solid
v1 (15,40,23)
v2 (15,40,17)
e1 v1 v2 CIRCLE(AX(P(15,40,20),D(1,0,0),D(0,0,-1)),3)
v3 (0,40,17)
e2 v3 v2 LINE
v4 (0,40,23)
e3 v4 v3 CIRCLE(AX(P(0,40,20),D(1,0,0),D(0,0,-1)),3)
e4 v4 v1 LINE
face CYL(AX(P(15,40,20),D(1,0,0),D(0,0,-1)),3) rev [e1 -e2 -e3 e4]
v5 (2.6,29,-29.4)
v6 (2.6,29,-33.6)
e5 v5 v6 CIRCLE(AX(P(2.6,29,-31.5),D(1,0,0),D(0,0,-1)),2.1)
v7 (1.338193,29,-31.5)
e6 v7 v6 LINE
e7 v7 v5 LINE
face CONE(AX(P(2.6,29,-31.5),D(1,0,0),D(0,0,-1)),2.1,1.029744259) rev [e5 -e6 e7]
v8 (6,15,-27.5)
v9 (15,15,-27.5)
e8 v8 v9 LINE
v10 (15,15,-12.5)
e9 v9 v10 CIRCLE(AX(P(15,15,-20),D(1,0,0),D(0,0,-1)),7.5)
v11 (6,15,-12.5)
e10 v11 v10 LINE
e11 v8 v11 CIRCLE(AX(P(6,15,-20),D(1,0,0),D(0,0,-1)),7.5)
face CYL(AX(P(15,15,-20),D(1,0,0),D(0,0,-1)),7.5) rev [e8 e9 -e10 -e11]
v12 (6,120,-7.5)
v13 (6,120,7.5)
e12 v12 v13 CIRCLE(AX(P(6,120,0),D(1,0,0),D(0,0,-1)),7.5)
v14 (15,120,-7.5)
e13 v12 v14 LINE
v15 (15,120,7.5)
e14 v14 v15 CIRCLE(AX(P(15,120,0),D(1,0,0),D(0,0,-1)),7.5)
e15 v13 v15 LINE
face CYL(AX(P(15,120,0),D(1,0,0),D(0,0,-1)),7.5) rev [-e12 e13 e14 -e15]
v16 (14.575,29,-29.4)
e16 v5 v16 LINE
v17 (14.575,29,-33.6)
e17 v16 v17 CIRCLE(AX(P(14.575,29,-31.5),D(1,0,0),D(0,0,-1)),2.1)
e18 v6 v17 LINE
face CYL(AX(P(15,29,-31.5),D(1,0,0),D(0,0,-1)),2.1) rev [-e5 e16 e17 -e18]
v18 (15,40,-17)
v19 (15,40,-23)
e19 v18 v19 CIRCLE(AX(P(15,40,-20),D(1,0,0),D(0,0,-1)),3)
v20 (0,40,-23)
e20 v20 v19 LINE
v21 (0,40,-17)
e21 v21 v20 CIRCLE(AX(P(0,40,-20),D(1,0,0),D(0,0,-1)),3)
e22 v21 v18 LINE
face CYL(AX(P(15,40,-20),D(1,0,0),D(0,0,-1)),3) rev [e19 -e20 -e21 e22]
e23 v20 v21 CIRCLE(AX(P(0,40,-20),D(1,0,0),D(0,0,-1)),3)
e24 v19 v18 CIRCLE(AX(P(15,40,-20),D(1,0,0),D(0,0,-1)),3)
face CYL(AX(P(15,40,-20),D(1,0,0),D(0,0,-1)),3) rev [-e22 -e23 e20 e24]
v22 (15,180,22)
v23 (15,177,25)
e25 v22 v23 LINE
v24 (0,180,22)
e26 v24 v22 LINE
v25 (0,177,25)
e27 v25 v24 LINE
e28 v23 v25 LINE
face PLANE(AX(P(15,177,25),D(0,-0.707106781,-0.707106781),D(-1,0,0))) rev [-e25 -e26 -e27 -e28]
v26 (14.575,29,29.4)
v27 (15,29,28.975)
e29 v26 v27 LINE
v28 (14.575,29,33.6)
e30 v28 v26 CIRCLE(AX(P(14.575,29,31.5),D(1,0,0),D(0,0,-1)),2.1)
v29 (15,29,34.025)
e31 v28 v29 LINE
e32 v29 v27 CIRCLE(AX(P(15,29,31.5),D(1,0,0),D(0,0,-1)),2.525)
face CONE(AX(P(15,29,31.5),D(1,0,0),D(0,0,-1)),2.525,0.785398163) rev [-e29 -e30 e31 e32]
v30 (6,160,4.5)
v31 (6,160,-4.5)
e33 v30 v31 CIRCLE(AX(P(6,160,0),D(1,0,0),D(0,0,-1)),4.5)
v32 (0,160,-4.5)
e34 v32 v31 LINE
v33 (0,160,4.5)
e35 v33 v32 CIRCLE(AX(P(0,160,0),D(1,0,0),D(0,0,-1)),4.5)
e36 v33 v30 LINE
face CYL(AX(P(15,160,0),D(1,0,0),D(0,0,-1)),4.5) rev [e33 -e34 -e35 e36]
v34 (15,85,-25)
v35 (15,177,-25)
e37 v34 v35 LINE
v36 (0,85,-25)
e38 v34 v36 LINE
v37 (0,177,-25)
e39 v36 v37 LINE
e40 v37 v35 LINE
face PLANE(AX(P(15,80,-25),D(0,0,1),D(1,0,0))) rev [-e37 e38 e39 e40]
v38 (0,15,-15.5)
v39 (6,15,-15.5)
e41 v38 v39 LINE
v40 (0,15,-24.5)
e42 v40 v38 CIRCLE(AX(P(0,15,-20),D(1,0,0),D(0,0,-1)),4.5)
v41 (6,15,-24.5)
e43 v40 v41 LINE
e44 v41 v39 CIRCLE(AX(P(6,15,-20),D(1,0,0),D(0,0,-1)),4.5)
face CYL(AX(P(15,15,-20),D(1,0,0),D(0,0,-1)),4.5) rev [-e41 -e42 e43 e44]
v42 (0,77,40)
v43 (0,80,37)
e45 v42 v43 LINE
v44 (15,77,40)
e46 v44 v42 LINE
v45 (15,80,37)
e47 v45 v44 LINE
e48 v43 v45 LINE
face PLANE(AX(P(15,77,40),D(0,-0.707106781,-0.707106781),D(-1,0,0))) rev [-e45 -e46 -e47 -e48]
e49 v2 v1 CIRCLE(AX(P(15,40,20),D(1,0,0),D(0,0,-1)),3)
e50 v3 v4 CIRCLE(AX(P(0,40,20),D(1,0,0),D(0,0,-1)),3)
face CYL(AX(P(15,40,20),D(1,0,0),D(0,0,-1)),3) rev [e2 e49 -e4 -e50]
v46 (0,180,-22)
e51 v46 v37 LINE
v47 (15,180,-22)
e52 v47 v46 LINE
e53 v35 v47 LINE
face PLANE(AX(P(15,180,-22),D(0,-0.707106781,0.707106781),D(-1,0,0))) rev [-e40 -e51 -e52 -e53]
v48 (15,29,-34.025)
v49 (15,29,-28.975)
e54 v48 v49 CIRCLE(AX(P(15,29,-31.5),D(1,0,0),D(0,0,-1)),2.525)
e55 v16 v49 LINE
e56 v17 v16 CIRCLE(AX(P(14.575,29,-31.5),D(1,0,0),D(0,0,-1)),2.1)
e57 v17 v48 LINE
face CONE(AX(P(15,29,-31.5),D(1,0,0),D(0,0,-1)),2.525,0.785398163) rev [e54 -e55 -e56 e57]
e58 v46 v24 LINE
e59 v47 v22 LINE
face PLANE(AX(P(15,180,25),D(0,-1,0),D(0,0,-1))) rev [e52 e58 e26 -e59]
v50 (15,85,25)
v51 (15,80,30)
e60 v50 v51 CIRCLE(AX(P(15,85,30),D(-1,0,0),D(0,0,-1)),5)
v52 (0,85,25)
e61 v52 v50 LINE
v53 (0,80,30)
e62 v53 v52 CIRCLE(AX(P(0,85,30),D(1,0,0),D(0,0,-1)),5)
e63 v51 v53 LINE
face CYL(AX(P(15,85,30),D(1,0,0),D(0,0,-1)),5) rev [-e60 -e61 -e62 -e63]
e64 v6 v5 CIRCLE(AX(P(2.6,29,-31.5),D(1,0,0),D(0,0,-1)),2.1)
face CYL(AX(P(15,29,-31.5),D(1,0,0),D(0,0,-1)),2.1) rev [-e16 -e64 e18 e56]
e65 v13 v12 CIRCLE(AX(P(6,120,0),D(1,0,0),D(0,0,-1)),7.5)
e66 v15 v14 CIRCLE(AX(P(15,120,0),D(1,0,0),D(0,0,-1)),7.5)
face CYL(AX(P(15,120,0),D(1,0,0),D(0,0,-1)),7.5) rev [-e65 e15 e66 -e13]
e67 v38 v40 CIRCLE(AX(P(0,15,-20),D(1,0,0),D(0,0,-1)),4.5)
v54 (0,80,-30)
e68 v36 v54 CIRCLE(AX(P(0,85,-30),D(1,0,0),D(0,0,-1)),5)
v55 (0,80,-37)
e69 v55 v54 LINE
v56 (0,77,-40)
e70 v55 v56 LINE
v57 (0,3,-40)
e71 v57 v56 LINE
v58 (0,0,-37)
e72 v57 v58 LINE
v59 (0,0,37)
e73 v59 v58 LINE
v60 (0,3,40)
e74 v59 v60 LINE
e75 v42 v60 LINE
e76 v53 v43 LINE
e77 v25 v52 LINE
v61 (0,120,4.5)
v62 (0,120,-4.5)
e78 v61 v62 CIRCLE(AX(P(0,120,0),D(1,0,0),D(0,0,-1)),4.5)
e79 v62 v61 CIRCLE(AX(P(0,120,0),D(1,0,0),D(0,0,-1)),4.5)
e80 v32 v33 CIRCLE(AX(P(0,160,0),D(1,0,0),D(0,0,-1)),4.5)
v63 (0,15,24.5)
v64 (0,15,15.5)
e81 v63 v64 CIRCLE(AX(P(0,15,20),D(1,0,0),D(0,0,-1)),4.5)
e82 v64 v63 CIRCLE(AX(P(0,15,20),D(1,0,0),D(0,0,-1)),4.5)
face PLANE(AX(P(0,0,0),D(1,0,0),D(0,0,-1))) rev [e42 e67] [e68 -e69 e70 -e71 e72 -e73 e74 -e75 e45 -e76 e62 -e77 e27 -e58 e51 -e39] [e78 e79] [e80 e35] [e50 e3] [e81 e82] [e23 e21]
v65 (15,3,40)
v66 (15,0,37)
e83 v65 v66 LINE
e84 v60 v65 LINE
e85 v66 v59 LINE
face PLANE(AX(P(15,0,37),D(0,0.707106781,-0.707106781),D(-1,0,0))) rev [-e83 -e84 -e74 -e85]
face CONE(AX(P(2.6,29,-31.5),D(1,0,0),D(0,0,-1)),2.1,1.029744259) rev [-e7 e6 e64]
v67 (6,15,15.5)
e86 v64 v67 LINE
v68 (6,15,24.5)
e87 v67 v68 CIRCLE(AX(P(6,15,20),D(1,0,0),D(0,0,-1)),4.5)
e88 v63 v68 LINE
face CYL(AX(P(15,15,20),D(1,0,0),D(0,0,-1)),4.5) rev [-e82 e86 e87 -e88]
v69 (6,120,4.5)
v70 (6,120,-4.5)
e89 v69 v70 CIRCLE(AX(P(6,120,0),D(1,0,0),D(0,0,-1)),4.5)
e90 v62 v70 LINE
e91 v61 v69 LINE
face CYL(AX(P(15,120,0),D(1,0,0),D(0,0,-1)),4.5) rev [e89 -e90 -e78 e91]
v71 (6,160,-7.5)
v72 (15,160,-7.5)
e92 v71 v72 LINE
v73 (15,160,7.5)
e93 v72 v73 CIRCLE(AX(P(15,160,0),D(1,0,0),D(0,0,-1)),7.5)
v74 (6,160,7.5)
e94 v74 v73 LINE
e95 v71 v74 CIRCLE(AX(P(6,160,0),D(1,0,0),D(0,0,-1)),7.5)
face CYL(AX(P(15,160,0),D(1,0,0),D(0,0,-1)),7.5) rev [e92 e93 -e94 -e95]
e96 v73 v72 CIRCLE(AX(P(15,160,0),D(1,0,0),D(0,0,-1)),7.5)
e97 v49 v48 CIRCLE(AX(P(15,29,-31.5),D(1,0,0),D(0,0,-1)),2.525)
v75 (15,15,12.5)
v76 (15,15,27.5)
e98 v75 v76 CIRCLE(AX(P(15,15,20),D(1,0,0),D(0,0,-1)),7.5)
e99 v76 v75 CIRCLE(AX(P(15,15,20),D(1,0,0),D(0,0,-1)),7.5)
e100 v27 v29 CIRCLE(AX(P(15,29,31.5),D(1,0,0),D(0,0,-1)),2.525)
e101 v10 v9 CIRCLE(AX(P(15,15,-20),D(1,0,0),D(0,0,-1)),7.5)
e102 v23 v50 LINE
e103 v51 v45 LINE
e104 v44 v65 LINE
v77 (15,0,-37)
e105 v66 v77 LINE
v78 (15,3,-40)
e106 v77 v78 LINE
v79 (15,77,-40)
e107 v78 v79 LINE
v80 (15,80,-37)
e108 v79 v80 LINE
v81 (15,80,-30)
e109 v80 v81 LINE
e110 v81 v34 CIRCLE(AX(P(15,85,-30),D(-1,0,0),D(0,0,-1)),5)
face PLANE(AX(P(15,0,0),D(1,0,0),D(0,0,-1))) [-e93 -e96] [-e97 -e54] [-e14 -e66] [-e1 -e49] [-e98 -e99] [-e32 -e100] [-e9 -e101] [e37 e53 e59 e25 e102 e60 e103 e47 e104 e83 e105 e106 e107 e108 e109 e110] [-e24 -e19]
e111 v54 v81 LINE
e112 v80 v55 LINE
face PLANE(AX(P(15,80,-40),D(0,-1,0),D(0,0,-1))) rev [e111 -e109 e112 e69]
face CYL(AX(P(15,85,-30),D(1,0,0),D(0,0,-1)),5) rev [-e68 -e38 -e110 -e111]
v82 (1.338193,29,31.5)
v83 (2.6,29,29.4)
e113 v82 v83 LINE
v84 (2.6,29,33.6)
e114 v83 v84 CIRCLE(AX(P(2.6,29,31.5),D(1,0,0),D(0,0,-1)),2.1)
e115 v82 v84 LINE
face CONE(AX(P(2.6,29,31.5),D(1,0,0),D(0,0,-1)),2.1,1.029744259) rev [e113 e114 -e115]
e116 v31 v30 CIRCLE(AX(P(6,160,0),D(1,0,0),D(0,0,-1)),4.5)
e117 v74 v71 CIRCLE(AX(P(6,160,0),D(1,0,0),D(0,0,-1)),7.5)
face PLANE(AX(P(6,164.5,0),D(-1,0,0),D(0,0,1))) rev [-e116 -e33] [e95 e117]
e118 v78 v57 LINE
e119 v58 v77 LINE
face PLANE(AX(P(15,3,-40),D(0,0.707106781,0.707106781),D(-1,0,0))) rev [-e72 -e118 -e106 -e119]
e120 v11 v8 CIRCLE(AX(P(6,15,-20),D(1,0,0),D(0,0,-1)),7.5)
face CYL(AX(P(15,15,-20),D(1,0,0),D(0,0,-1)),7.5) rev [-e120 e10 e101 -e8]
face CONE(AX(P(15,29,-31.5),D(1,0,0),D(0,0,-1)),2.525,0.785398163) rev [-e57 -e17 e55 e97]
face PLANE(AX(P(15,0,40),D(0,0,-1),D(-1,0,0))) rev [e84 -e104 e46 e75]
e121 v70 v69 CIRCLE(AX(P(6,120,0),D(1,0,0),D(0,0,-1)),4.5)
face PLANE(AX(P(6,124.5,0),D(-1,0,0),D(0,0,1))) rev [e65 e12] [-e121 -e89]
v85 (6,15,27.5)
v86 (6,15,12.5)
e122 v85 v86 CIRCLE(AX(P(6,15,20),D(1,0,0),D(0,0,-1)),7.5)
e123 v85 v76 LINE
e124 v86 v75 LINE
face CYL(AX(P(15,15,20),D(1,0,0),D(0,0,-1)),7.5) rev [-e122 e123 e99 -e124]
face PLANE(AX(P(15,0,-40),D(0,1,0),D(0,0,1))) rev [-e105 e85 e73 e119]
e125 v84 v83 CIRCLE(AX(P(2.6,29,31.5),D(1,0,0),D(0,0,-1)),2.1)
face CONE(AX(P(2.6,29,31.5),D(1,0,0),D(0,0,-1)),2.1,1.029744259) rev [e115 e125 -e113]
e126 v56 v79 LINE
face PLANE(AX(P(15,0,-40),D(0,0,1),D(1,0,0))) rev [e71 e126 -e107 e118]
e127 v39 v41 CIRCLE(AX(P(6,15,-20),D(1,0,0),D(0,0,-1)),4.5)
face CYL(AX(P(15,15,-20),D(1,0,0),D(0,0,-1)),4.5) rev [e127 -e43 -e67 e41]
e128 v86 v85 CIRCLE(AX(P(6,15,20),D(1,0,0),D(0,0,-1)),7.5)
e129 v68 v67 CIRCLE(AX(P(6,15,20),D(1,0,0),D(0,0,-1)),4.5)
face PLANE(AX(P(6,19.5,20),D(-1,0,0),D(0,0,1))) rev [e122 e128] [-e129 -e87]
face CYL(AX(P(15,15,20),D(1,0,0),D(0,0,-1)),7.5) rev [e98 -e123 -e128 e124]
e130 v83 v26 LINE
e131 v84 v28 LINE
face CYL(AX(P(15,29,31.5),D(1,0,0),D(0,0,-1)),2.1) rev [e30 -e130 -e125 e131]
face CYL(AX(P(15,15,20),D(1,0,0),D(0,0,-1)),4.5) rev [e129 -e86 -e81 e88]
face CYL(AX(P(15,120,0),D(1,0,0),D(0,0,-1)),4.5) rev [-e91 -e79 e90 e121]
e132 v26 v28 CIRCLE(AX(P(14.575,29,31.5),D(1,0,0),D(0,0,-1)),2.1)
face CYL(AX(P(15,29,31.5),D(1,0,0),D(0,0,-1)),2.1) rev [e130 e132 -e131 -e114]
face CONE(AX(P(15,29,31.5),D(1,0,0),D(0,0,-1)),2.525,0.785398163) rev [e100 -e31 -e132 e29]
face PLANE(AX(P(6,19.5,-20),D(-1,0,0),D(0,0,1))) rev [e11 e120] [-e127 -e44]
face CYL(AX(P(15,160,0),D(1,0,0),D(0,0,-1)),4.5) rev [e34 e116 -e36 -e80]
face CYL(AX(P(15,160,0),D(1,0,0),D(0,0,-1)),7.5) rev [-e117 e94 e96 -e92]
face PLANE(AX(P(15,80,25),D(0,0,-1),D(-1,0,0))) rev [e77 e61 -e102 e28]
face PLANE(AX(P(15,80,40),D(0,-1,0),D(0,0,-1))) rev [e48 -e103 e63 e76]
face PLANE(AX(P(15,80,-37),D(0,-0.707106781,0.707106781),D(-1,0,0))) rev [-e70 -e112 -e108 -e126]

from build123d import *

# Parameters (mm, degrees)
BOSS_EXTRUDE1_DEPTH                                  = 15
M5_TAPPED_HOLE1_D                                    = 4.2
M5_TAPPED_HOLE1_DEPTH                                = 12.4
M5_TAPPED_HOLE1_CSINK_D                              = 5.05
M5_TAPPED_HOLE1_CSINK_ANGLE                          = 90
M5_TAPPED_HOLE1_TIP                                  = 1.2618073
CBORE_FOR_M8_HEXAGON_SOCKET_HEAD_CAP_SCR_D           = 9
CBORE_FOR_M8_HEXAGON_SOCKET_HEAD_CAP_SCR_CBORE_D     = 15
CBORE_FOR_M8_HEXAGON_SOCKET_HEAD_CAP_SCR_CBORE_DEPTH = 9
CBORE_FOR_M8_HEXAGON_SOCKET_HEAD_CAP_2_D             = 9
CBORE_FOR_M8_HEXAGON_SOCKET_HEAD_CAP_2_CBORE_D       = 15
CBORE_FOR_M8_HEXAGON_SOCKET_HEAD_CAP_2_CBORE_DEPTH   = 9
F_6_0MM_BLIND_HOLE_1_D                               = 6
FILLET1_R                                            = 5
CHAMFER1_SIZE                                        = 3


with BuildPart() as part:
    # Sketch1 → Boss-Extrude1 (new body)
    with BuildSketch(Plane(origin=(0, 0, 0), x_dir=(0, 0, -1), z_dir=(1, 0, 0))):
        Polygon((40, 0), (-40, 0), (-40, 80), (-25, 80), (-25, 180), (25, 180), (25, 80), (40, 80), align=None)
    extrude(amount=BOSS_EXTRUDE1_DEPTH)

    # M5 Tapped Hole1
    with Locations(Plane(origin=(15, 0, 0), x_dir=(0, 0, -1), z_dir=(1, 0, 0))):
        with Locations((31.5, 29), (-31.5, 29)):
            CounterSinkHole(M5_TAPPED_HOLE1_D / 2, M5_TAPPED_HOLE1_CSINK_D / 2, depth=M5_TAPPED_HOLE1_DEPTH, counter_sink_angle=M5_TAPPED_HOLE1_CSINK_ANGLE)
            with Locations((0, 0, -(M5_TAPPED_HOLE1_DEPTH + M5_TAPPED_HOLE1_TIP / 2))):  # 118° drill point
                Cone(0, M5_TAPPED_HOLE1_D / 2, M5_TAPPED_HOLE1_TIP, mode=Mode.SUBTRACT)

    # CBORE for M8 Hexagon socket head cap scr (through all)
    with Locations(Plane(origin=(15, 0, 0), x_dir=(0, 0, -1), z_dir=(1, 0, 0))):
        with Locations((0, 160), (0, 120)):
            CounterBoreHole(CBORE_FOR_M8_HEXAGON_SOCKET_HEAD_CAP_SCR_D / 2, CBORE_FOR_M8_HEXAGON_SOCKET_HEAD_CAP_SCR_CBORE_D / 2, CBORE_FOR_M8_HEXAGON_SOCKET_HEAD_CAP_SCR_CBORE_DEPTH)

    # CBORE for M8 Hexagon socket head cap 2 (through all)
    with Locations(Plane(origin=(15, 0, 0), x_dir=(0, 0, -1), z_dir=(1, 0, 0))):
        with Locations((-20, 15), (20, 15)):
            CounterBoreHole(CBORE_FOR_M8_HEXAGON_SOCKET_HEAD_CAP_2_D / 2, CBORE_FOR_M8_HEXAGON_SOCKET_HEAD_CAP_2_CBORE_D / 2, CBORE_FOR_M8_HEXAGON_SOCKET_HEAD_CAP_2_CBORE_DEPTH)

    # Ø6.0mm blind hole 1 (through all)
    with Locations(Plane(origin=(15, 0, 0), x_dir=(0, 0, -1), z_dir=(1, 0, 0))):
        with Locations((-20, 40), (20, 40)):
            Hole(F_6_0MM_BLIND_HOLE_1_D / 2)

    # Fillet1
    fillet1_edges = [part.edges().sort_by_distance(p)[0] for p in [
        (7.5, 80, 25),
        (7.5, 80, -25),
    ]]
    fillet(fillet1_edges, radius=FILLET1_R)

    # Chamfer1
    chamfer1_edges = [part.edges().sort_by_distance(p)[0] for p in [
        (7.5, 180, 25),
        (7.5, 180, -25),
        (7.5, 80, -40),
        (7.5, 0, -40),
        (7.5, 0, 40),
        (7.5, 80, 40),
    ]]
    chamfer(chamfer1_edges, length=CHAMFER1_SIZE)


solid = part.part
